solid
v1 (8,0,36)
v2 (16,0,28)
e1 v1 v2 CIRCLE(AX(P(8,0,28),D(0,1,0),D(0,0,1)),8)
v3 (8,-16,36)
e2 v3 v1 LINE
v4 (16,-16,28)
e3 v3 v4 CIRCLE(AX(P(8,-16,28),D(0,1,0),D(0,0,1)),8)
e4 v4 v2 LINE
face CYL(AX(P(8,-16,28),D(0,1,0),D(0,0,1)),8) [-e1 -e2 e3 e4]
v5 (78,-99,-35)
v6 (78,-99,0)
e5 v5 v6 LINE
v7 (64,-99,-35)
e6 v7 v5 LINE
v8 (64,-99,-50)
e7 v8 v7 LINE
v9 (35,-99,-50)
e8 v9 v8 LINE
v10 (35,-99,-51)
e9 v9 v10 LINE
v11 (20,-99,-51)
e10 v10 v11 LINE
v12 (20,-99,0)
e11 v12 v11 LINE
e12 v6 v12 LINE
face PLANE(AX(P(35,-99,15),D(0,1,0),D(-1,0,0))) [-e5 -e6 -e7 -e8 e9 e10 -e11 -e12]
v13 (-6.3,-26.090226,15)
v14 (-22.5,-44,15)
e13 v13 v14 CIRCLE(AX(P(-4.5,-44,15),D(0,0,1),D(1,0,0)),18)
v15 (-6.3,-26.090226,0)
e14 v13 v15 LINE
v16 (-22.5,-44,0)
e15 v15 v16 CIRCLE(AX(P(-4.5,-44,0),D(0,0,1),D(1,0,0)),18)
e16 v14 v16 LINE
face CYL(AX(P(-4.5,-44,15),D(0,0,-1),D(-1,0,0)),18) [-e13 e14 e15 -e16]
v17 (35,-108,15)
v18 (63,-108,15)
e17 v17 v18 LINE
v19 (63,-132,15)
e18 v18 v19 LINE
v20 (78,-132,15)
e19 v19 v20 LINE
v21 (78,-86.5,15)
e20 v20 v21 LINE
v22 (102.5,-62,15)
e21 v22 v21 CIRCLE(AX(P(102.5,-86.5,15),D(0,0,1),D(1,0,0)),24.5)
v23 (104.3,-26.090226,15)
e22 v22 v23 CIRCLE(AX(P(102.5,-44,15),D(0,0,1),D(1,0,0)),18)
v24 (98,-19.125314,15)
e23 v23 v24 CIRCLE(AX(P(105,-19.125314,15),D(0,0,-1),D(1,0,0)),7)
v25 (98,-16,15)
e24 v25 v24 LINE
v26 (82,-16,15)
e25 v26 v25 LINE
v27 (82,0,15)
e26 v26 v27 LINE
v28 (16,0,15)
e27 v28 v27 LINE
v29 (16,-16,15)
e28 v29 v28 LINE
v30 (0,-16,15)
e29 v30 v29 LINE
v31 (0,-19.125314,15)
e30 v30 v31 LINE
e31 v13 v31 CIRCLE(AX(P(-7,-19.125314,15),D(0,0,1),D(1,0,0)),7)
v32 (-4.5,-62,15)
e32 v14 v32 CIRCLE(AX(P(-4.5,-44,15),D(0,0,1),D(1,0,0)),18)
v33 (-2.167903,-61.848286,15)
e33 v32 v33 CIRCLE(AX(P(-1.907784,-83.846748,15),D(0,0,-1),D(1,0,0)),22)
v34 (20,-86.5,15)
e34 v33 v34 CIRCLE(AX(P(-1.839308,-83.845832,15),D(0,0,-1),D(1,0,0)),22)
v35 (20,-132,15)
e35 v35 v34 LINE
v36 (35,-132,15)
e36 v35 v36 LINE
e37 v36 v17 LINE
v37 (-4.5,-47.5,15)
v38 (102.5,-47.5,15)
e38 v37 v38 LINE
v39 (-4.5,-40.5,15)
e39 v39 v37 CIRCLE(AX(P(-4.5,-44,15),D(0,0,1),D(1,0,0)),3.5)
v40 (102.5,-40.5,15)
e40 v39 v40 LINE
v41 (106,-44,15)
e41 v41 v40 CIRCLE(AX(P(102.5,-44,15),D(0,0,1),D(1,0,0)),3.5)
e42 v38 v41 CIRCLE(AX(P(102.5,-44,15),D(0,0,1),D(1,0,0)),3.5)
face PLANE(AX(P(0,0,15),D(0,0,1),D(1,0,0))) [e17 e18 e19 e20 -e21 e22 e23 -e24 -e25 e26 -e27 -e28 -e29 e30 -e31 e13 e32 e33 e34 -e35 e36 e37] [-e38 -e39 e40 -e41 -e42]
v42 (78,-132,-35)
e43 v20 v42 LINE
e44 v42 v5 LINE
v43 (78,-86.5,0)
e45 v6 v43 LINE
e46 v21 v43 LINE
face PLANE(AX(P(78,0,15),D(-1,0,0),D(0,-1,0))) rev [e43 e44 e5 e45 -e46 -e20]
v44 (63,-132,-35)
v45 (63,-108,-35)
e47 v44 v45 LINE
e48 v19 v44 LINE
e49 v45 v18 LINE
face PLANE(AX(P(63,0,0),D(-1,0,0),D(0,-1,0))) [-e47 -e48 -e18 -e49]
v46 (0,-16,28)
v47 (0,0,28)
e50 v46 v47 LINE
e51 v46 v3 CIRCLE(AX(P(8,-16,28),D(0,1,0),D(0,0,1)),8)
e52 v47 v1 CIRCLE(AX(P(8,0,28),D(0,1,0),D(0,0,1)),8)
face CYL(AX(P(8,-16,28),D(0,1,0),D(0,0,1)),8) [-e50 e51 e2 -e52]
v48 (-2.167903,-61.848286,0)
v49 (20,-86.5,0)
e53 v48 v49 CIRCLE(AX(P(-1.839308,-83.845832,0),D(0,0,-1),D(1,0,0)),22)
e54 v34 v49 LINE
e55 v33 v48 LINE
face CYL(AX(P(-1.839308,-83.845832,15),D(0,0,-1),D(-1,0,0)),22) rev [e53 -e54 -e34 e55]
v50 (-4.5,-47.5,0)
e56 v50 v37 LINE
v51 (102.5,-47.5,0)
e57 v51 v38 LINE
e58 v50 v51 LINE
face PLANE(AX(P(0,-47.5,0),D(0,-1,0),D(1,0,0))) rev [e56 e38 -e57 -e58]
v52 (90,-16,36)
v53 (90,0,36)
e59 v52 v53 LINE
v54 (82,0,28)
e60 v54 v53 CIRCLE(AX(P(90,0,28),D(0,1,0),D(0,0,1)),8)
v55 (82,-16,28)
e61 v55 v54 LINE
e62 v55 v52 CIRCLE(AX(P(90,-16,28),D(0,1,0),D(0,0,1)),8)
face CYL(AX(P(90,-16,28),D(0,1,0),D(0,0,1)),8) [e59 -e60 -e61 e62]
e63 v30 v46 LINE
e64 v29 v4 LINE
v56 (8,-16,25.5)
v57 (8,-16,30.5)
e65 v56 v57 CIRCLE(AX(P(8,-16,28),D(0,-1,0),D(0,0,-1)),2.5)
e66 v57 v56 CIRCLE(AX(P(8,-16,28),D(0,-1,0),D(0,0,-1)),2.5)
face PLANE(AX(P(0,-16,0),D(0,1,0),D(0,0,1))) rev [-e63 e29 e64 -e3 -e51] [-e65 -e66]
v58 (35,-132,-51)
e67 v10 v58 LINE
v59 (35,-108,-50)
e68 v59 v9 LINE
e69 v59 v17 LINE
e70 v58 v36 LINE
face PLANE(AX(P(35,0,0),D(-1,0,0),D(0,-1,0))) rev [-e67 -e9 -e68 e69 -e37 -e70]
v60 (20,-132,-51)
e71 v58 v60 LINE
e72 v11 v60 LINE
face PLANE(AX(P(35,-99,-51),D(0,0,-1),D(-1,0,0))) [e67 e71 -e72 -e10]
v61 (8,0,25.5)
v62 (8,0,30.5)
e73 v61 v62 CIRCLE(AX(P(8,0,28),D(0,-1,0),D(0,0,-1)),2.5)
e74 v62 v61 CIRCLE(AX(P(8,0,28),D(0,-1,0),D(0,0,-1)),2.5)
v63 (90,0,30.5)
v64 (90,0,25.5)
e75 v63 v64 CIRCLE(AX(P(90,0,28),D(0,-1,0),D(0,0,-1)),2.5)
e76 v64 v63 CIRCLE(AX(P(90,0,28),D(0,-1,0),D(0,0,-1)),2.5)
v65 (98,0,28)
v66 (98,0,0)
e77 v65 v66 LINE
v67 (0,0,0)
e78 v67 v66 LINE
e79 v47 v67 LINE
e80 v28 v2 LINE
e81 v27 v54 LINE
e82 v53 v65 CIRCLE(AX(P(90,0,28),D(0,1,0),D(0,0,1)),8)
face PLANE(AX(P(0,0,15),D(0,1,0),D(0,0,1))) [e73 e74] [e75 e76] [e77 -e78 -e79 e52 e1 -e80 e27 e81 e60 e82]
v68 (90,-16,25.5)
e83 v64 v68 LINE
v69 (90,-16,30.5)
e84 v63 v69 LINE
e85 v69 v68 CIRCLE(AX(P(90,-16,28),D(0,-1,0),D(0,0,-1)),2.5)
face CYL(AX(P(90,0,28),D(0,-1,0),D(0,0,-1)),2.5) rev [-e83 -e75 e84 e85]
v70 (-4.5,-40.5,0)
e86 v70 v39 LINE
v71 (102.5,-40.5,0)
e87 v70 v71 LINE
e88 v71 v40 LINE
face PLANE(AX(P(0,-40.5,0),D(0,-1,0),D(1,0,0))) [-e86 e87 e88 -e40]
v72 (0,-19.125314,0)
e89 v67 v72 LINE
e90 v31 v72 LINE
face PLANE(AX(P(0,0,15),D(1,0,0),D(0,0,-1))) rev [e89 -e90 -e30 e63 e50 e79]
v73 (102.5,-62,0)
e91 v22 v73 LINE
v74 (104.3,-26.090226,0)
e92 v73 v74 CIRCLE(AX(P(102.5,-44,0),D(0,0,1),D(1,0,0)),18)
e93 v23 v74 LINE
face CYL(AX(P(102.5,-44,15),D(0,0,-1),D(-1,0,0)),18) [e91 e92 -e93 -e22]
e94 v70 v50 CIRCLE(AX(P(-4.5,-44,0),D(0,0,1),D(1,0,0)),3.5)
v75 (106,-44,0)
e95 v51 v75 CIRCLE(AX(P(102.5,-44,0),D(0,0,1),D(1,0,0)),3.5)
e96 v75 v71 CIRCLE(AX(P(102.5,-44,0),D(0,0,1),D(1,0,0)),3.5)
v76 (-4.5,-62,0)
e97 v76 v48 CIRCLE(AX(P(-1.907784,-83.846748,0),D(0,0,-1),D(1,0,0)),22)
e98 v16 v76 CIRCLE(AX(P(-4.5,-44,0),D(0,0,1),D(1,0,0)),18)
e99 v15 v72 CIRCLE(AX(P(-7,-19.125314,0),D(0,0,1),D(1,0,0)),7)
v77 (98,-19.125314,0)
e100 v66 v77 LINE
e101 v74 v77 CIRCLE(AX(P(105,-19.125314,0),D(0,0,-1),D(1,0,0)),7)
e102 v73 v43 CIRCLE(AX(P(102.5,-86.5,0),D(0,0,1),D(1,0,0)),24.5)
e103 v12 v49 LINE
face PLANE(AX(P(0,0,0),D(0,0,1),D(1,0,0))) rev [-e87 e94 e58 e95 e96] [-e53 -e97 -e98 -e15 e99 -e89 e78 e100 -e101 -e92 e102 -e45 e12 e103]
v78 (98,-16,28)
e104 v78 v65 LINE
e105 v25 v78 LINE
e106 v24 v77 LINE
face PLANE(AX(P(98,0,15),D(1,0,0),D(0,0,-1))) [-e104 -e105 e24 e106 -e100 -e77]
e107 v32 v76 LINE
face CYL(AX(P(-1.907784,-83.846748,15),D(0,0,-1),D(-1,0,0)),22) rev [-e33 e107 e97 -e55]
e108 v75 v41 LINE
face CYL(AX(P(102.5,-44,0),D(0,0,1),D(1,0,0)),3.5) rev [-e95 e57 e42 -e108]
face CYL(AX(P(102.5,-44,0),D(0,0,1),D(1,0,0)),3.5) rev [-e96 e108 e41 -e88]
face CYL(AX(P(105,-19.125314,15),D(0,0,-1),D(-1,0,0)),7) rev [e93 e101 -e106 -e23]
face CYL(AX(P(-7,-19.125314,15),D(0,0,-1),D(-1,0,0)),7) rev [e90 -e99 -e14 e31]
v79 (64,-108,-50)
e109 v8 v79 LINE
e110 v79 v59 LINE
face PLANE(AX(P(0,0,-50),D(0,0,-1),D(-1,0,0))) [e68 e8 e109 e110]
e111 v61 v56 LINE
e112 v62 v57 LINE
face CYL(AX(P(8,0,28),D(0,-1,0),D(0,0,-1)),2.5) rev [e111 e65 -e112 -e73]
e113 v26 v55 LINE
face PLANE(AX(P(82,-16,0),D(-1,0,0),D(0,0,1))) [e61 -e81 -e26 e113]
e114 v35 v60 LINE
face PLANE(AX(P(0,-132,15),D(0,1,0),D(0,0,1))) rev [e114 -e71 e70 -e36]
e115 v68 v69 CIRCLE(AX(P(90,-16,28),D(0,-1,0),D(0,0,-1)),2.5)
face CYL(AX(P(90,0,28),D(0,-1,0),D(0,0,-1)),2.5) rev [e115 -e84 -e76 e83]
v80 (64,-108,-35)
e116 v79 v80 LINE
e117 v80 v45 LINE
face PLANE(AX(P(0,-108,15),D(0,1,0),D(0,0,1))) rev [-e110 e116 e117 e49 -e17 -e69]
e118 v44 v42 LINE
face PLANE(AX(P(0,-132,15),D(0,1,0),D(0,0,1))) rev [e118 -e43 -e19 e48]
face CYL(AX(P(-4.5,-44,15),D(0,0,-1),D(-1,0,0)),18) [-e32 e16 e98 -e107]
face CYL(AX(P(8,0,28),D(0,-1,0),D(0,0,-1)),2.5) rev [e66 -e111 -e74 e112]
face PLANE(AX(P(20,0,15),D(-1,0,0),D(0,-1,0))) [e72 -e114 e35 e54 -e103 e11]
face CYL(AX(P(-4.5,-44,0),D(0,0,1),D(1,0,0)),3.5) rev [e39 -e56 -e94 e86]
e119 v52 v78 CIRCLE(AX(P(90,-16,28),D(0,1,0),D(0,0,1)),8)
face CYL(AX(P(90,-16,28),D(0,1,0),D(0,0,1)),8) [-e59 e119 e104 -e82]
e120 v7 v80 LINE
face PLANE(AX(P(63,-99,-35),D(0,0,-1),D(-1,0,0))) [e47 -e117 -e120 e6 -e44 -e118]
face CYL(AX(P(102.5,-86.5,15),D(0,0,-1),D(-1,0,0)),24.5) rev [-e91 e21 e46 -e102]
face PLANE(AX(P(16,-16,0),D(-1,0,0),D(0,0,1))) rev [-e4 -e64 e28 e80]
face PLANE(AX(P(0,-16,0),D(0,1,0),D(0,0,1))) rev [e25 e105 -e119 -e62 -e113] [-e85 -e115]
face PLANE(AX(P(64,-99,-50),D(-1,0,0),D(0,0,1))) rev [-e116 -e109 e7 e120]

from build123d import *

# Parameters (mm, degrees)
BASE_PLATE_DEPTH         = 15
LONG_SLOT_DEPTH          = 15
LOWER_BLOCK_SKETCH_W     = 66
LOWER_BLOCK_SKETCH_H     = 33
LOWER_BLOCK_33X66_DEPTH  = 15
BLOCK_EXTENSION_SKETCH_W = 29
BLOCK_EXTENSION_SKETCH_H = 9
BLOCK_EXTENSION_DEPTH    = 50
BLOCK_END_SKETCH_W       = 50
BLOCK_END_SKETCH_H       = 33
BLOCK_END_50X50_DEPTH    = 15
LUG_A_DEPTH              = 16
LUG_B_DEPTH              = 16
LUG_HOLES_SKETCH_R       = 2.5
LUG_HOLES_2X5MM_DEPTH    = 16


with BuildPart() as part:
    # Base Plate Profile Sketch → Base Plate (new body)
    with BuildSketch(Plane.XY):
        with BuildLine():
            Line((49, 0), (0, 0))
            Line((0, 0), (0, -19.125314072))
            ThreePointArc((0, -19.125314072), (-1.808661059, -23.821056825), (-6.3, -26.090226132))
            ThreePointArc((-6.3, -26.090226132), (-22.477429316, -44.901129951), (-4.5, -62))
            ThreePointArc((-4.5, -62), (-3.335967318, -61.893154357), (-2.167902709, -61.848286255))
            ThreePointArc((-2.167902709, -61.848286255), (14.519311725, -69.135443097), (20, -86.5))
            Line((20, -86.5), (20, -132))
            Line((20, -132), (34, -132))
            Line((34, -132), (34, -108))
            Line((34, -108), (64, -108))
            Line((64, -108), (64, -132))
            Line((64, -132), (78, -132))
            Line((78, -132), (78, -86.5))
            ThreePointArc((78, -86.5), (85.175883861, -69.175883861), (102.5, -62))
            ThreePointArc((102.5, -62), (120.477429316, -44.901129951), (104.3, -26.090226132))
            ThreePointArc((104.3, -26.090226132), (99.808661059, -23.821056825), (98, -19.125314072))
            Line((98, -19.125314072), (98, 0))
            Line((98, 0), (49, 0))
        make_face()
    extrude(amount=BASE_PLATE_DEPTH)

    # Long Slot Sketch → Long Slot (cut)
    with BuildSketch(Plane.XY.offset(15)):
        with BuildLine():
            Line((-4.5, -40.5), (102.5, -40.5))
            ThreePointArc((102.5, -40.5), (106, -44), (102.5, -47.5))
            Line((102.5, -47.5), (-4.5, -47.5))
            ThreePointArc((-4.5, -47.5), (-8, -44), (-4.5, -40.5))
        make_face()
    extrude(amount=-LONG_SLOT_DEPTH, mode=Mode.SUBTRACT)

    # Lower Block Sketch → Lower Block 33x66 (add)
    with BuildSketch(Plane.ZY.offset(-20)):
        with Locations((-18, -115.5)):
            Rectangle(LOWER_BLOCK_SKETCH_W, LOWER_BLOCK_SKETCH_H)
    extrude(amount=-LOWER_BLOCK_33X66_DEPTH)

    # Block Extension Sketch → Block Extension (add)
    with BuildSketch(Plane(origin=(0, 0, 0), x_dir=(-1, 0, 0), z_dir=(0, 0, -1))):
        with Locations((-49.5, -103.5)):
            Rectangle(BLOCK_EXTENSION_SKETCH_W, BLOCK_EXTENSION_SKETCH_H)
    extrude(amount=BLOCK_EXTENSION_DEPTH)

    # Block End Sketch → Block End 50x50 (add)
    with BuildSketch(Plane(origin=(78, 0, 0), x_dir=(0, 0, -1), z_dir=(1, 0, 0))):
        with Locations((10, -115.5)):
            Rectangle(BLOCK_END_SKETCH_W, BLOCK_END_SKETCH_H)
    extrude(amount=-BLOCK_END_50X50_DEPTH)

    # Lug A Sketch → Lug A (add)
    with BuildSketch(Plane(origin=(0, 0, 0), x_dir=(1, 0, 0), z_dir=(0, 1, 0))):
        with BuildLine():
            Line((8, -15), (0, -15))
            Line((0, -15), (0, -28))
            ThreePointArc((0, -28), (8, -36), (16, -28))
            Line((16, -28), (16, -15))
            Line((16, -15), (8, -15))
        make_face()
    extrude(amount=-LUG_A_DEPTH)

    # Lug B Sketch → Lug B (add)
    with BuildSketch(Plane(origin=(0, 0, 0), x_dir=(1, 0, 0), z_dir=(0, 1, 0))):
        with BuildLine():
            Line((98, -28), (98, -15))
            Line((98, -15), (90, -15))
            Line((90, -15), (82, -15))
            Line((82, -15), (82, -28))
            ThreePointArc((82, -28), (90, -36), (98, -28))
        make_face()
    extrude(amount=-LUG_B_DEPTH)

    # Lug Holes Sketch → Lug Holes 2x5mm (cut)
    with BuildSketch(Plane.XZ.offset(16)):
        with Locations(Location((90, 28, 0), (0, 0, 270))):
            Circle(LUG_HOLES_SKETCH_R)
        with Locations(Location((8, 28, 0), (0, 0, 270))):
            Circle(LUG_HOLES_SKETCH_R)
    extrude(amount=-LUG_HOLES_2X5MM_DEPTH, mode=Mode.SUBTRACT)


solid = part.part
